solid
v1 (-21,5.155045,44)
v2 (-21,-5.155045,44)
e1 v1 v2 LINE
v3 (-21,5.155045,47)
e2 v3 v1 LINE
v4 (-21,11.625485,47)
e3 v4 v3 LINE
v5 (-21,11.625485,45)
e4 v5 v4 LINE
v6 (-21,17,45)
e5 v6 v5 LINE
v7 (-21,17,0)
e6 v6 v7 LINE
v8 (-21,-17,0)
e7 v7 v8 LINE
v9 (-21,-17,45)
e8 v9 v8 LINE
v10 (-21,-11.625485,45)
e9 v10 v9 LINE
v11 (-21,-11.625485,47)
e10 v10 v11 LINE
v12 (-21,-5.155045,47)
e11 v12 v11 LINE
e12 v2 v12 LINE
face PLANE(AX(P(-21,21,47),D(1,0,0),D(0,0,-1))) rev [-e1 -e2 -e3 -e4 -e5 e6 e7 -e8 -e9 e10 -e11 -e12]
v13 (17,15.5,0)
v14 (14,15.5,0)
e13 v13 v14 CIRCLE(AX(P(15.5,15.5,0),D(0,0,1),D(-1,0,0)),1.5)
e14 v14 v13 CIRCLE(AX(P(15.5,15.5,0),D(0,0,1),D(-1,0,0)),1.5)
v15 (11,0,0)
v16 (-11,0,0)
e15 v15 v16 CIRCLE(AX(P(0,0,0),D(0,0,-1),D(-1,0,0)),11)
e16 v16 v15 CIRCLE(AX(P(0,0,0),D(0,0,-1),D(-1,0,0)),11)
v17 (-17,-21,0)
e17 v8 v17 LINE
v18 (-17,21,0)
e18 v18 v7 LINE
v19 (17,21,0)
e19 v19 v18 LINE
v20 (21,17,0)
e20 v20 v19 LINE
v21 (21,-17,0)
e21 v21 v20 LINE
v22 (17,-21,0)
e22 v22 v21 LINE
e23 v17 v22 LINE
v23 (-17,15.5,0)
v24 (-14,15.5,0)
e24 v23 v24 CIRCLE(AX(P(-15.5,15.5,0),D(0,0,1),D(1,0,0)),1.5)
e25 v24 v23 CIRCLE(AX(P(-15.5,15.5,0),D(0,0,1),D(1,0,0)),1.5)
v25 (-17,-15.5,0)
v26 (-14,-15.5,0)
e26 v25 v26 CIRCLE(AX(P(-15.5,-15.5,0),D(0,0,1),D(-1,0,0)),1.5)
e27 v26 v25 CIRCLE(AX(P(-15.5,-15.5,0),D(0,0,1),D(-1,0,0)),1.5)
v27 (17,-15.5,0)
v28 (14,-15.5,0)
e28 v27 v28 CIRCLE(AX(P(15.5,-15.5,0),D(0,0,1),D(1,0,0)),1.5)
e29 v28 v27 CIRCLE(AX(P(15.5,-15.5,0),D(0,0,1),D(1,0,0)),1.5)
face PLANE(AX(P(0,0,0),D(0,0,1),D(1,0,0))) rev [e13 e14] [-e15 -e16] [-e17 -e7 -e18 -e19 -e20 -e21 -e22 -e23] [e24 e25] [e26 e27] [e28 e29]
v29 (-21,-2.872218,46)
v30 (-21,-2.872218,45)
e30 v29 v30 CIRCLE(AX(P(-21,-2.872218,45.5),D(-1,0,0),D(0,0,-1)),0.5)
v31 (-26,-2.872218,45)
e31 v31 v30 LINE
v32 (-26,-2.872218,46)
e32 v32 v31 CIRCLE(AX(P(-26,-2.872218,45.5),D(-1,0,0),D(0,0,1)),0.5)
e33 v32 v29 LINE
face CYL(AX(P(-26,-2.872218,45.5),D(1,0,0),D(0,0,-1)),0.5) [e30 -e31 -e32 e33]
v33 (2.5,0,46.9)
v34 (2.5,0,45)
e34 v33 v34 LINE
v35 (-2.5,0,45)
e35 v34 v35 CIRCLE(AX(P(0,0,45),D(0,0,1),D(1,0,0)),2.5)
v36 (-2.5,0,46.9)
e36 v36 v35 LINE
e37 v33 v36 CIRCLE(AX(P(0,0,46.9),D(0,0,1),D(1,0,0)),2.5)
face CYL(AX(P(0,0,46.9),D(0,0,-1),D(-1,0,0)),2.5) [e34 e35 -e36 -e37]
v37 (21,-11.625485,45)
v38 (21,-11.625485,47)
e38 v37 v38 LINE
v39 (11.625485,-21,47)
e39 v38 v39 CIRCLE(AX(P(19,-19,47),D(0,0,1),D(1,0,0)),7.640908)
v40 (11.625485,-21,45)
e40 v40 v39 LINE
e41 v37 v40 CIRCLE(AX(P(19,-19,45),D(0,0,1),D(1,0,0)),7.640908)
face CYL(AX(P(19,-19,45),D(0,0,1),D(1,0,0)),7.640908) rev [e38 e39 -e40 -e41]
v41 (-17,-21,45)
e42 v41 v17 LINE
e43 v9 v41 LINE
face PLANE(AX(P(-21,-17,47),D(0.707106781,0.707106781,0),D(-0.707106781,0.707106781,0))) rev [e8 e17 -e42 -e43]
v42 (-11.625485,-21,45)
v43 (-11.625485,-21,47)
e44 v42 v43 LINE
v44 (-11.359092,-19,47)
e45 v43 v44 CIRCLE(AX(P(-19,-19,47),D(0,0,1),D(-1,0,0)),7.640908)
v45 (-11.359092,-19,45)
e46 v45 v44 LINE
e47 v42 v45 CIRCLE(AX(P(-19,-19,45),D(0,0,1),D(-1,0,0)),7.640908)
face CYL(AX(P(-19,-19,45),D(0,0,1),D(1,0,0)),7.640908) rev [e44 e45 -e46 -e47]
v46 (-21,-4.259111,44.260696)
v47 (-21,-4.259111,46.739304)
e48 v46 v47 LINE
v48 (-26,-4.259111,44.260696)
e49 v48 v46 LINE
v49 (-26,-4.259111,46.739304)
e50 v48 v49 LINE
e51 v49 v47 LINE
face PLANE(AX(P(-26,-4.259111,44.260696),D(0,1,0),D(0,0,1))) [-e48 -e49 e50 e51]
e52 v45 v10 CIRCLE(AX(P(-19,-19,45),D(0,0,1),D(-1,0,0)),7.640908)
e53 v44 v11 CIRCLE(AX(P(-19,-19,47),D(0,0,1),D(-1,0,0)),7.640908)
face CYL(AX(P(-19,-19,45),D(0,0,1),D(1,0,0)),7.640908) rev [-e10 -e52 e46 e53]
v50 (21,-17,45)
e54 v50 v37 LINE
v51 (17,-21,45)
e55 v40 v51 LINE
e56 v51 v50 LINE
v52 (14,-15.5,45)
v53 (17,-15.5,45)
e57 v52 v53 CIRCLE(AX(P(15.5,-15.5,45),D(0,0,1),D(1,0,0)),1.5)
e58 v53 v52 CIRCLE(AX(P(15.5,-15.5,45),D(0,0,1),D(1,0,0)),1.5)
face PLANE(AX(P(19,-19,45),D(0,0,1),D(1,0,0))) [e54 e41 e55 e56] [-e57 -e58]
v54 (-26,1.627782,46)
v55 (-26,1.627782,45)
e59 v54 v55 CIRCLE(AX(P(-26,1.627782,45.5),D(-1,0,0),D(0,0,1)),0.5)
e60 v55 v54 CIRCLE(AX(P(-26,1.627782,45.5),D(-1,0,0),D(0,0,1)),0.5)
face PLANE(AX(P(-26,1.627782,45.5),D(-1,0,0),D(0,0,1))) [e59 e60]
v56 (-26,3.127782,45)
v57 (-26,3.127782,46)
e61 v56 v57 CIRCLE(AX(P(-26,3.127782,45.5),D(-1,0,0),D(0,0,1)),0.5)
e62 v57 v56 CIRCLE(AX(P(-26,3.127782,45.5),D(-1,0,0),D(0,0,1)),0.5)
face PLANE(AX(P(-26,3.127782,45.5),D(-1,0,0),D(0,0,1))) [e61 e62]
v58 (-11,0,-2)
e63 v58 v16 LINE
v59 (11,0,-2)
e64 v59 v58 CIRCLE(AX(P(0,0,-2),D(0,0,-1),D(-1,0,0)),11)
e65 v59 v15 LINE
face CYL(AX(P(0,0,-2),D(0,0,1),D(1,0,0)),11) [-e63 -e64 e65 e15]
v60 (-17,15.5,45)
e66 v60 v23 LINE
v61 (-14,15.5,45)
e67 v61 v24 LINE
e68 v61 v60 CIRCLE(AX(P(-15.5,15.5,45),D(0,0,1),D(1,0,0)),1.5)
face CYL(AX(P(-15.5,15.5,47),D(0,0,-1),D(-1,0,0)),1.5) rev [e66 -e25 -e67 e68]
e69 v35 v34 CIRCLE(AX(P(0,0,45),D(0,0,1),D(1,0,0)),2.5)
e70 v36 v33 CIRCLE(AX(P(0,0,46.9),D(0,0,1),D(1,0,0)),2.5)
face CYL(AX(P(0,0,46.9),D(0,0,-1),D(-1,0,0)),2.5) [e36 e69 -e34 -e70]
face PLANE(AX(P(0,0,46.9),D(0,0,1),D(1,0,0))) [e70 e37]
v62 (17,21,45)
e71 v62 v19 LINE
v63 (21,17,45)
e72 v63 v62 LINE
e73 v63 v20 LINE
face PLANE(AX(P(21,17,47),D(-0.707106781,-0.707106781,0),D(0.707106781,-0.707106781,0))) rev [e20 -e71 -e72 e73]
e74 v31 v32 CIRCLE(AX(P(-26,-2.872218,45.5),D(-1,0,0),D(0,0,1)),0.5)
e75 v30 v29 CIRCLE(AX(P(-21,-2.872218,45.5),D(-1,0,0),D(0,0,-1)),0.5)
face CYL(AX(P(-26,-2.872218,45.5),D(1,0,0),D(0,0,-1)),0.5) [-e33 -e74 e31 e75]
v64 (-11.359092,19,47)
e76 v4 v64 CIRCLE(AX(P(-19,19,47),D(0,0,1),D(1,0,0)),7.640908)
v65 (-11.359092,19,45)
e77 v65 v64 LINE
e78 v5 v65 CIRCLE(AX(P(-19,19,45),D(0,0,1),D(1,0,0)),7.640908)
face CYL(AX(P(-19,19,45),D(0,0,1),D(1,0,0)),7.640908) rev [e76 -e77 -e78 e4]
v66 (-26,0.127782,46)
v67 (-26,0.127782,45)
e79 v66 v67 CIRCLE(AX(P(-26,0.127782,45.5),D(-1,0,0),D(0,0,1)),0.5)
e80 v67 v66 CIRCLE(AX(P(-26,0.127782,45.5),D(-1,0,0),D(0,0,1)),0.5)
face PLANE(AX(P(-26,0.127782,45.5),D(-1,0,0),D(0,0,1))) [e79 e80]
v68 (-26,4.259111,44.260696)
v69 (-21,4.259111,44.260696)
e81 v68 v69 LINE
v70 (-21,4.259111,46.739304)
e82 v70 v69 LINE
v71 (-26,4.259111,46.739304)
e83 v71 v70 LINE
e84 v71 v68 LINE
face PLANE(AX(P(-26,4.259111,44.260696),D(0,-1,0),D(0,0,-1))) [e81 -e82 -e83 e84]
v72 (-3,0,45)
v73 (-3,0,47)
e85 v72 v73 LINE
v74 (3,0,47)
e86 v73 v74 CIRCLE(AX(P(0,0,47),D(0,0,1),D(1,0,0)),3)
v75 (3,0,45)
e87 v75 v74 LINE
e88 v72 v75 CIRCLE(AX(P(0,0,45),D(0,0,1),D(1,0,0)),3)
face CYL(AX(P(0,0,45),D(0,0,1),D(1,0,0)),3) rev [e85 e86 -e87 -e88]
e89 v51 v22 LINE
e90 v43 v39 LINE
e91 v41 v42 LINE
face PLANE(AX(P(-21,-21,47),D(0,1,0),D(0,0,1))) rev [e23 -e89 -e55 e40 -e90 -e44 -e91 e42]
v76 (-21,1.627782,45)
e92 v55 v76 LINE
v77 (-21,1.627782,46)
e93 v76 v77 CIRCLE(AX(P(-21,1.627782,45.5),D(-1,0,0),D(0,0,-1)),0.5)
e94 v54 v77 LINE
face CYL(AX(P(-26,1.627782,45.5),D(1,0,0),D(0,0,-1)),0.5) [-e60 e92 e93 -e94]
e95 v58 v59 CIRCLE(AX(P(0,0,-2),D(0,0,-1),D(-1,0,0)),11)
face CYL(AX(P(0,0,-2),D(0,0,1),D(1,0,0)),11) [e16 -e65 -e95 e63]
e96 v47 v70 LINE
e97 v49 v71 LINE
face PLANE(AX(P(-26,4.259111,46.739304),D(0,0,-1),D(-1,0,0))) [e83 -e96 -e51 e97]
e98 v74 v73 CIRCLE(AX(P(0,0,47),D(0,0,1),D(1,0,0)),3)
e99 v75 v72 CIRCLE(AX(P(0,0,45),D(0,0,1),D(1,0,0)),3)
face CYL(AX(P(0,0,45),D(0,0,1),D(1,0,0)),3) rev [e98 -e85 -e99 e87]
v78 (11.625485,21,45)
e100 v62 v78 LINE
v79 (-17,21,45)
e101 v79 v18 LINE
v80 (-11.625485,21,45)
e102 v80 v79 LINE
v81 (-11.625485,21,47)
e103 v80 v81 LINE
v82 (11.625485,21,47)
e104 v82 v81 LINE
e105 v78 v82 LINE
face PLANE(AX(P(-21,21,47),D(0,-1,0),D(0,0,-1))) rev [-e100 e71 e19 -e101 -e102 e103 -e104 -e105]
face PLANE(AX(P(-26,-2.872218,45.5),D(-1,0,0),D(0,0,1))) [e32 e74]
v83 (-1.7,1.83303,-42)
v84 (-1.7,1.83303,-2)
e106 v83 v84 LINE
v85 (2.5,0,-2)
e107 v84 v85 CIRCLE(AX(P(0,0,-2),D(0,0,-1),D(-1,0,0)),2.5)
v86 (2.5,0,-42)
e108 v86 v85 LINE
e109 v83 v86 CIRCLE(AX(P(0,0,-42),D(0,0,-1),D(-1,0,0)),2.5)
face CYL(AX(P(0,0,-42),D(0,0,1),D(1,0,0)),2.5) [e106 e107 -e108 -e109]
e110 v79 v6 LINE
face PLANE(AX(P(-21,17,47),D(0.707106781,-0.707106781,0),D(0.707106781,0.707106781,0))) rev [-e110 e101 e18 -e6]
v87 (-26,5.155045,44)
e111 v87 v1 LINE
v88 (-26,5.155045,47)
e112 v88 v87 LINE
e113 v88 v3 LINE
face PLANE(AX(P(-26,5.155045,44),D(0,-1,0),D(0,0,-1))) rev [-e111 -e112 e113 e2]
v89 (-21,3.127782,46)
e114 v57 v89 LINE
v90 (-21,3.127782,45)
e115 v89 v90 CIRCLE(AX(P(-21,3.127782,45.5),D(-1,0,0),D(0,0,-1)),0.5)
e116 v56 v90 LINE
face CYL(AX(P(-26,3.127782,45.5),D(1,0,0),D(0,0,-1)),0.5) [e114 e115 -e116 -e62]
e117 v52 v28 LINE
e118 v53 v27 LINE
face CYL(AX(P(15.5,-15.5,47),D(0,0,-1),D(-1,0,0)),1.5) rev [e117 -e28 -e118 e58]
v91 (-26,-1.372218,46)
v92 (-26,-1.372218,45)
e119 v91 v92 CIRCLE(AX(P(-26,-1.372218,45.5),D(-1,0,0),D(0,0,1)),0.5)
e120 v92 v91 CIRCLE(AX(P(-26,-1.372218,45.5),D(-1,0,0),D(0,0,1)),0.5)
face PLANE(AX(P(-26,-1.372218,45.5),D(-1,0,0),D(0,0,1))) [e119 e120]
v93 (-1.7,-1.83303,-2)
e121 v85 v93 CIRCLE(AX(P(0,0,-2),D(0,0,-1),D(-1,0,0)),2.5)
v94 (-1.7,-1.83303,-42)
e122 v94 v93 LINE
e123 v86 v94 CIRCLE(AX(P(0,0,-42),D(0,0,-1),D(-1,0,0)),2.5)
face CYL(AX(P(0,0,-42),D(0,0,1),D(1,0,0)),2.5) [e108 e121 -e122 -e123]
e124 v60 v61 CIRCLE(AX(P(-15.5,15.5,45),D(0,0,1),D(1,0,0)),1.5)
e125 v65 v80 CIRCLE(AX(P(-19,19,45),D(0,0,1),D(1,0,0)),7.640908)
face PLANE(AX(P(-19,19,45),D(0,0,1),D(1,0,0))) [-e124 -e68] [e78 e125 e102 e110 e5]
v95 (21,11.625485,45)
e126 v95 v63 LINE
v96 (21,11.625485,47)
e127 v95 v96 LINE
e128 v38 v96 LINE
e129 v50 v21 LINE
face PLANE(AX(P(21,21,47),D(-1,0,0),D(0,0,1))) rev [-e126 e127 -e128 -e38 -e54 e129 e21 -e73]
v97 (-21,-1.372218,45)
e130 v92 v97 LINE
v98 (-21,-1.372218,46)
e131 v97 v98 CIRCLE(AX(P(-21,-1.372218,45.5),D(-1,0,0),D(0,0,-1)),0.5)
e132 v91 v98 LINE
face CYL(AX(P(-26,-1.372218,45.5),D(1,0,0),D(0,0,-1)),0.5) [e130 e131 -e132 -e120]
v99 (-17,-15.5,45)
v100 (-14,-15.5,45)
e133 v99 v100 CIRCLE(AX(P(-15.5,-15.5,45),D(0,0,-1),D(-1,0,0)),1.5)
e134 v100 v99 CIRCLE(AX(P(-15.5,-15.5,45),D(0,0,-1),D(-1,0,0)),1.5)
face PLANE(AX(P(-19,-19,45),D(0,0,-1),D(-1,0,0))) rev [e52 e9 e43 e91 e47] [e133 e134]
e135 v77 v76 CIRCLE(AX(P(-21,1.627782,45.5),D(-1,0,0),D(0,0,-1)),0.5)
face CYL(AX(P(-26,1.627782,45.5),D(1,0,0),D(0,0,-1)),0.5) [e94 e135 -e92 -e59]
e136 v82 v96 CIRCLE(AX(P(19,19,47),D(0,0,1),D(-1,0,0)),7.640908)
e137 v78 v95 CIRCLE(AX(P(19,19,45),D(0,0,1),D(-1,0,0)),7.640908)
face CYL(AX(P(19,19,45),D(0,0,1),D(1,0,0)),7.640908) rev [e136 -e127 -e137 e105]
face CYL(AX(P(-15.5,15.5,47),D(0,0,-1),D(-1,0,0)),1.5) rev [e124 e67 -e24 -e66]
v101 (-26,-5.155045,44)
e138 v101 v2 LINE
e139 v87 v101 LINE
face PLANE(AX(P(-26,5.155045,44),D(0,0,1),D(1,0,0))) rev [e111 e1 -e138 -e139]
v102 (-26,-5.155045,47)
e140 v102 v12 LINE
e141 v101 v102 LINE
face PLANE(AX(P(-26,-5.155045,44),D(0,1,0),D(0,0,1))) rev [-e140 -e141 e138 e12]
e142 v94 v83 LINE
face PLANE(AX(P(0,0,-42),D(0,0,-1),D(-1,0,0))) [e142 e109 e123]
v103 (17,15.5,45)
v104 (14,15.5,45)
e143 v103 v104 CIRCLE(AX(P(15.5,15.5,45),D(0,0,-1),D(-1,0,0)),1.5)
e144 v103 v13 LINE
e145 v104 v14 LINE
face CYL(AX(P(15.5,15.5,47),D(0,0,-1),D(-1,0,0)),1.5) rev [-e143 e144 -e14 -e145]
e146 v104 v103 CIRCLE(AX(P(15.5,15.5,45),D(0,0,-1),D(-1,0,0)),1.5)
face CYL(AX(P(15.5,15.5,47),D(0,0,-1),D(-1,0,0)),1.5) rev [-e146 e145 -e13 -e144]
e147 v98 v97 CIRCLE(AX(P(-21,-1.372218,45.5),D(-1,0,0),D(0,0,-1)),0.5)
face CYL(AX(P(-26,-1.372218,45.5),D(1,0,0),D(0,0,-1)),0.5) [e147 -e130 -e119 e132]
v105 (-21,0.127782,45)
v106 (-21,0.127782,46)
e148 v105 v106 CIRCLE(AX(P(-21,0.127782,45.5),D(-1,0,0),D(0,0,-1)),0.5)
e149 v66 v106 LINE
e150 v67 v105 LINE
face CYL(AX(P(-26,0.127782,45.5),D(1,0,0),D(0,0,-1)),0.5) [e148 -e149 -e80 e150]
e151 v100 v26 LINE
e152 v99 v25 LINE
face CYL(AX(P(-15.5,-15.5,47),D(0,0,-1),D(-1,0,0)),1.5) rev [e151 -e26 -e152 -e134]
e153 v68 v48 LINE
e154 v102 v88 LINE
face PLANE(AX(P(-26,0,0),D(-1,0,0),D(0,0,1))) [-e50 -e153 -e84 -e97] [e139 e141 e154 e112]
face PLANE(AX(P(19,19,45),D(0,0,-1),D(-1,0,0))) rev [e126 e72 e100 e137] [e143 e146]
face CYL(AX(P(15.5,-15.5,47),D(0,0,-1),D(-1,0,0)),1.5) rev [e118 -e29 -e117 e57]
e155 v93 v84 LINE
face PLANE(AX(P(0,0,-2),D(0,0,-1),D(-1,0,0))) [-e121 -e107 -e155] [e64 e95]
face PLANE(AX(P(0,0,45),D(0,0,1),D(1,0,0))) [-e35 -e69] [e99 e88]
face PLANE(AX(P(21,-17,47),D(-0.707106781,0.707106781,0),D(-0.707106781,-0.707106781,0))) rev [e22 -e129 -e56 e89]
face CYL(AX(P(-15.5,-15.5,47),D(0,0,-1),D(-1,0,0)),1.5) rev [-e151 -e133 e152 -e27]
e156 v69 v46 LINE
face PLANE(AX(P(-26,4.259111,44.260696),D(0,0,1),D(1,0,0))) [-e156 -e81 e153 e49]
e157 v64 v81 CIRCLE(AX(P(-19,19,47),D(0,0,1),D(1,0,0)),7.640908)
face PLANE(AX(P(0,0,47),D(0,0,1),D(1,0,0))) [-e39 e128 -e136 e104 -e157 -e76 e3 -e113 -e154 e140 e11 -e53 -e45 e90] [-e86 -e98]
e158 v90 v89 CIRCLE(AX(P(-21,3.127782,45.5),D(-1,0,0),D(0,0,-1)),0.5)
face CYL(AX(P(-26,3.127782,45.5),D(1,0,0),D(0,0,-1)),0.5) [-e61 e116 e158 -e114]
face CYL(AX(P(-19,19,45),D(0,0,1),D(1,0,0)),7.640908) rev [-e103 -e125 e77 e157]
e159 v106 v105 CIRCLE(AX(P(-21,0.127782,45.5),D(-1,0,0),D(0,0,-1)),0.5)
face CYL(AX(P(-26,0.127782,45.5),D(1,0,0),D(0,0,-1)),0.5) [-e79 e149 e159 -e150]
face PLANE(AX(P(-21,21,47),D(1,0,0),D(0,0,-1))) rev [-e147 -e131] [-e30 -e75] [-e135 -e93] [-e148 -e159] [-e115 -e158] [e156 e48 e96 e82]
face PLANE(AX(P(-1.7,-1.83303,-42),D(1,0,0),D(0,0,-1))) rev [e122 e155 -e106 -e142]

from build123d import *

# Parameters (mm, degrees)
SKETCH1_W           = 42
SKETCH1_H           = 42
SKETCH1_R           = 1.5
BOSS_EXTRUDE1_DEPTH = 47
CUT_EXTRUDE1_DEPTH  = 56.596762496
SKETCH4_R           = 11
BOSS_EXTRUDE2_DEPTH = 2
BOSS_EXTRUDE3_DEPTH = 40
CUT_EXTRUDE2_DEPTH  = 2
SKETCH8_R           = 3
CUT_EXTRUDE3_DEPTH  = 2
BOSS_EXTRUDE4_START = 1.9
SKETCH9_R           = 2.5
BOSS_EXTRUDE4_DEPTH = 1.9
SKETCH10_W          = 3
SKETCH10_H          = 10.31009041
SKETCH10_W_2        = 2.478607588
SKETCH10_H_2        = 8.518222776
BOSS_EXTRUDE5_DEPTH = 5
SKETCH11_R          = 0.5
BOSS_EXTRUDE6_DEPTH = 5


with BuildPart() as part:
    # Sketch1 → Boss-Extrude1 (new body)
    with BuildSketch(Plane.XY):
        Rectangle(SKETCH1_W, SKETCH1_H)
        with Locations((-15.5, 15.5)):
            Circle(SKETCH1_R, mode=Mode.SUBTRACT)
        with Locations(Location((15.5, 15.5, 0), (0, 0, 180))):
            Circle(SKETCH1_R, mode=Mode.SUBTRACT)
        with Locations(Location((-15.5, -15.5, 0), (0, 0, 180))):
            Circle(SKETCH1_R, mode=Mode.SUBTRACT)
        with Locations((15.5, -15.5)):
            Circle(SKETCH1_R, mode=Mode.SUBTRACT)
    extrude(amount=BOSS_EXTRUDE1_DEPTH)

    # Sketch3 → Cut-Extrude1 (cut, through all)
    with BuildSketch(Plane(origin=(0, 0, 0), x_dir=(-1, 0, 0), z_dir=(0, 0, -1))):
        Polygon((-21, 17), (-17, 21), (-21, 21), align=None)
        Polygon((21, 21), (17, 21), (21, 17), align=None)
        Polygon((21, -17), (17, -21), (21, -21), align=None)
        Polygon((-21, -21), (-17, -21), (-21, -17), align=None)
    extrude(amount=-CUT_EXTRUDE1_DEPTH, mode=Mode.SUBTRACT)

    # Sketch4 → Boss-Extrude2 (add)
    with BuildSketch(Plane(origin=(0, 0, 0), x_dir=(-1, 0, 0), z_dir=(0, 0, -1))):
        Circle(SKETCH4_R)
    extrude(amount=BOSS_EXTRUDE2_DEPTH)

    # Sketch5 → Boss-Extrude3 (add)
    with BuildSketch(Plane(origin=(0, 0, -2), x_dir=(-1, 0, 0), z_dir=(0, 0, -1))):
        with BuildLine():
            Line((1.7, -1.833030278), (1.7, 1.833030278))
            ThreePointArc((1.7, 1.833030278), (-2.5, 0), (1.7, -1.833030278))
        make_face()
    extrude(amount=BOSS_EXTRUDE3_DEPTH)

    # Sketch7 → Cut-Extrude2 (cut)
    with BuildSketch(Plane.XY.offset(47)):
        with BuildLine():
            Line((21, 17), (21, 11.625484678))
            ThreePointArc((21, 11.625484678), (13.597062084, 13.597062084), (11.625484678, 21))
            Line((11.625484678, 21), (17, 21))
            Line((17, 21), (21, 17))
        make_face()
        with BuildLine():
            Line((-21, -17), (-21, -11.625484678))
            ThreePointArc((-21, -11.625484678), (-13.597062084, -13.597062084), (-11.625484678, -21))
            Line((-11.625484678, -21), (-17, -21))
            Line((-17, -21), (-21, -17))
        make_face()
        with BuildLine():
            Line((-11.625484678, 21), (-17, 21))
            Line((-17, 21), (-21, 17))
            Line((-21, 17), (-21, 11.625484678))
            ThreePointArc((-21, 11.625484678), (-13.597062084, 13.597062084), (-11.625484678, 21))
        make_face()
        with BuildLine():
            Line((11.625484678, -21), (17, -21))
            Line((17, -21), (21, -17))
            Line((21, -17), (21, -11.625484678))
            ThreePointArc((21, -11.625484678), (13.597062084, -13.597062084), (11.625484678, -21))
        make_face()
    extrude(amount=-CUT_EXTRUDE2_DEPTH, mode=Mode.SUBTRACT)

    # Sketch8 → Cut-Extrude3 (cut)
    with BuildSketch(Plane.XY.offset(47)):
        Circle(SKETCH8_R)
    extrude(amount=-CUT_EXTRUDE3_DEPTH, mode=Mode.SUBTRACT)

    # Sketch9 → Boss-Extrude4 (add)
    with BuildSketch(Plane.XY.offset(45).offset(BOSS_EXTRUDE4_START)):
        with Locations(Location((0, 0, 0), (0, 0, 180))):
            Circle(SKETCH9_R)
    extrude(amount=-BOSS_EXTRUDE4_DEPTH)

    # Sketch10 → Boss-Extrude5 (add)
    with BuildSketch(Plane.ZY.offset(21)):
        with Locations((45.5, 0)):
            Rectangle(SKETCH10_W, SKETCH10_H)
        with Locations((45.5, 0)):
            Rectangle(SKETCH10_W_2, SKETCH10_H_2, mode=Mode.SUBTRACT)
    extrude(amount=BOSS_EXTRUDE5_DEPTH)

    # Sketch11 → Boss-Extrude6 (add)
    with BuildSketch(Plane.ZY.offset(21)):
        with Locations(Location((45.5, 3.127782029, 0), (0, 0, 180))):
            Circle(SKETCH11_R)
        with Locations(Location((45.5, 1.627782029, 0), (0, 0, 180))):
            Circle(SKETCH11_R)
        with Locations(Location((45.5, 0.127782029, 0), (0, 0, 180))):
            Circle(SKETCH11_R)
        with Locations(Location((45.5, -1.372217971, 0), (0, 0, 180))):
            Circle(SKETCH11_R)
        with Locations(Location((45.5, -2.872217971, 0), (0, 0, 180))):
            Circle(SKETCH11_R)
    extrude(amount=BOSS_EXTRUDE6_DEPTH)


solid = part.part
